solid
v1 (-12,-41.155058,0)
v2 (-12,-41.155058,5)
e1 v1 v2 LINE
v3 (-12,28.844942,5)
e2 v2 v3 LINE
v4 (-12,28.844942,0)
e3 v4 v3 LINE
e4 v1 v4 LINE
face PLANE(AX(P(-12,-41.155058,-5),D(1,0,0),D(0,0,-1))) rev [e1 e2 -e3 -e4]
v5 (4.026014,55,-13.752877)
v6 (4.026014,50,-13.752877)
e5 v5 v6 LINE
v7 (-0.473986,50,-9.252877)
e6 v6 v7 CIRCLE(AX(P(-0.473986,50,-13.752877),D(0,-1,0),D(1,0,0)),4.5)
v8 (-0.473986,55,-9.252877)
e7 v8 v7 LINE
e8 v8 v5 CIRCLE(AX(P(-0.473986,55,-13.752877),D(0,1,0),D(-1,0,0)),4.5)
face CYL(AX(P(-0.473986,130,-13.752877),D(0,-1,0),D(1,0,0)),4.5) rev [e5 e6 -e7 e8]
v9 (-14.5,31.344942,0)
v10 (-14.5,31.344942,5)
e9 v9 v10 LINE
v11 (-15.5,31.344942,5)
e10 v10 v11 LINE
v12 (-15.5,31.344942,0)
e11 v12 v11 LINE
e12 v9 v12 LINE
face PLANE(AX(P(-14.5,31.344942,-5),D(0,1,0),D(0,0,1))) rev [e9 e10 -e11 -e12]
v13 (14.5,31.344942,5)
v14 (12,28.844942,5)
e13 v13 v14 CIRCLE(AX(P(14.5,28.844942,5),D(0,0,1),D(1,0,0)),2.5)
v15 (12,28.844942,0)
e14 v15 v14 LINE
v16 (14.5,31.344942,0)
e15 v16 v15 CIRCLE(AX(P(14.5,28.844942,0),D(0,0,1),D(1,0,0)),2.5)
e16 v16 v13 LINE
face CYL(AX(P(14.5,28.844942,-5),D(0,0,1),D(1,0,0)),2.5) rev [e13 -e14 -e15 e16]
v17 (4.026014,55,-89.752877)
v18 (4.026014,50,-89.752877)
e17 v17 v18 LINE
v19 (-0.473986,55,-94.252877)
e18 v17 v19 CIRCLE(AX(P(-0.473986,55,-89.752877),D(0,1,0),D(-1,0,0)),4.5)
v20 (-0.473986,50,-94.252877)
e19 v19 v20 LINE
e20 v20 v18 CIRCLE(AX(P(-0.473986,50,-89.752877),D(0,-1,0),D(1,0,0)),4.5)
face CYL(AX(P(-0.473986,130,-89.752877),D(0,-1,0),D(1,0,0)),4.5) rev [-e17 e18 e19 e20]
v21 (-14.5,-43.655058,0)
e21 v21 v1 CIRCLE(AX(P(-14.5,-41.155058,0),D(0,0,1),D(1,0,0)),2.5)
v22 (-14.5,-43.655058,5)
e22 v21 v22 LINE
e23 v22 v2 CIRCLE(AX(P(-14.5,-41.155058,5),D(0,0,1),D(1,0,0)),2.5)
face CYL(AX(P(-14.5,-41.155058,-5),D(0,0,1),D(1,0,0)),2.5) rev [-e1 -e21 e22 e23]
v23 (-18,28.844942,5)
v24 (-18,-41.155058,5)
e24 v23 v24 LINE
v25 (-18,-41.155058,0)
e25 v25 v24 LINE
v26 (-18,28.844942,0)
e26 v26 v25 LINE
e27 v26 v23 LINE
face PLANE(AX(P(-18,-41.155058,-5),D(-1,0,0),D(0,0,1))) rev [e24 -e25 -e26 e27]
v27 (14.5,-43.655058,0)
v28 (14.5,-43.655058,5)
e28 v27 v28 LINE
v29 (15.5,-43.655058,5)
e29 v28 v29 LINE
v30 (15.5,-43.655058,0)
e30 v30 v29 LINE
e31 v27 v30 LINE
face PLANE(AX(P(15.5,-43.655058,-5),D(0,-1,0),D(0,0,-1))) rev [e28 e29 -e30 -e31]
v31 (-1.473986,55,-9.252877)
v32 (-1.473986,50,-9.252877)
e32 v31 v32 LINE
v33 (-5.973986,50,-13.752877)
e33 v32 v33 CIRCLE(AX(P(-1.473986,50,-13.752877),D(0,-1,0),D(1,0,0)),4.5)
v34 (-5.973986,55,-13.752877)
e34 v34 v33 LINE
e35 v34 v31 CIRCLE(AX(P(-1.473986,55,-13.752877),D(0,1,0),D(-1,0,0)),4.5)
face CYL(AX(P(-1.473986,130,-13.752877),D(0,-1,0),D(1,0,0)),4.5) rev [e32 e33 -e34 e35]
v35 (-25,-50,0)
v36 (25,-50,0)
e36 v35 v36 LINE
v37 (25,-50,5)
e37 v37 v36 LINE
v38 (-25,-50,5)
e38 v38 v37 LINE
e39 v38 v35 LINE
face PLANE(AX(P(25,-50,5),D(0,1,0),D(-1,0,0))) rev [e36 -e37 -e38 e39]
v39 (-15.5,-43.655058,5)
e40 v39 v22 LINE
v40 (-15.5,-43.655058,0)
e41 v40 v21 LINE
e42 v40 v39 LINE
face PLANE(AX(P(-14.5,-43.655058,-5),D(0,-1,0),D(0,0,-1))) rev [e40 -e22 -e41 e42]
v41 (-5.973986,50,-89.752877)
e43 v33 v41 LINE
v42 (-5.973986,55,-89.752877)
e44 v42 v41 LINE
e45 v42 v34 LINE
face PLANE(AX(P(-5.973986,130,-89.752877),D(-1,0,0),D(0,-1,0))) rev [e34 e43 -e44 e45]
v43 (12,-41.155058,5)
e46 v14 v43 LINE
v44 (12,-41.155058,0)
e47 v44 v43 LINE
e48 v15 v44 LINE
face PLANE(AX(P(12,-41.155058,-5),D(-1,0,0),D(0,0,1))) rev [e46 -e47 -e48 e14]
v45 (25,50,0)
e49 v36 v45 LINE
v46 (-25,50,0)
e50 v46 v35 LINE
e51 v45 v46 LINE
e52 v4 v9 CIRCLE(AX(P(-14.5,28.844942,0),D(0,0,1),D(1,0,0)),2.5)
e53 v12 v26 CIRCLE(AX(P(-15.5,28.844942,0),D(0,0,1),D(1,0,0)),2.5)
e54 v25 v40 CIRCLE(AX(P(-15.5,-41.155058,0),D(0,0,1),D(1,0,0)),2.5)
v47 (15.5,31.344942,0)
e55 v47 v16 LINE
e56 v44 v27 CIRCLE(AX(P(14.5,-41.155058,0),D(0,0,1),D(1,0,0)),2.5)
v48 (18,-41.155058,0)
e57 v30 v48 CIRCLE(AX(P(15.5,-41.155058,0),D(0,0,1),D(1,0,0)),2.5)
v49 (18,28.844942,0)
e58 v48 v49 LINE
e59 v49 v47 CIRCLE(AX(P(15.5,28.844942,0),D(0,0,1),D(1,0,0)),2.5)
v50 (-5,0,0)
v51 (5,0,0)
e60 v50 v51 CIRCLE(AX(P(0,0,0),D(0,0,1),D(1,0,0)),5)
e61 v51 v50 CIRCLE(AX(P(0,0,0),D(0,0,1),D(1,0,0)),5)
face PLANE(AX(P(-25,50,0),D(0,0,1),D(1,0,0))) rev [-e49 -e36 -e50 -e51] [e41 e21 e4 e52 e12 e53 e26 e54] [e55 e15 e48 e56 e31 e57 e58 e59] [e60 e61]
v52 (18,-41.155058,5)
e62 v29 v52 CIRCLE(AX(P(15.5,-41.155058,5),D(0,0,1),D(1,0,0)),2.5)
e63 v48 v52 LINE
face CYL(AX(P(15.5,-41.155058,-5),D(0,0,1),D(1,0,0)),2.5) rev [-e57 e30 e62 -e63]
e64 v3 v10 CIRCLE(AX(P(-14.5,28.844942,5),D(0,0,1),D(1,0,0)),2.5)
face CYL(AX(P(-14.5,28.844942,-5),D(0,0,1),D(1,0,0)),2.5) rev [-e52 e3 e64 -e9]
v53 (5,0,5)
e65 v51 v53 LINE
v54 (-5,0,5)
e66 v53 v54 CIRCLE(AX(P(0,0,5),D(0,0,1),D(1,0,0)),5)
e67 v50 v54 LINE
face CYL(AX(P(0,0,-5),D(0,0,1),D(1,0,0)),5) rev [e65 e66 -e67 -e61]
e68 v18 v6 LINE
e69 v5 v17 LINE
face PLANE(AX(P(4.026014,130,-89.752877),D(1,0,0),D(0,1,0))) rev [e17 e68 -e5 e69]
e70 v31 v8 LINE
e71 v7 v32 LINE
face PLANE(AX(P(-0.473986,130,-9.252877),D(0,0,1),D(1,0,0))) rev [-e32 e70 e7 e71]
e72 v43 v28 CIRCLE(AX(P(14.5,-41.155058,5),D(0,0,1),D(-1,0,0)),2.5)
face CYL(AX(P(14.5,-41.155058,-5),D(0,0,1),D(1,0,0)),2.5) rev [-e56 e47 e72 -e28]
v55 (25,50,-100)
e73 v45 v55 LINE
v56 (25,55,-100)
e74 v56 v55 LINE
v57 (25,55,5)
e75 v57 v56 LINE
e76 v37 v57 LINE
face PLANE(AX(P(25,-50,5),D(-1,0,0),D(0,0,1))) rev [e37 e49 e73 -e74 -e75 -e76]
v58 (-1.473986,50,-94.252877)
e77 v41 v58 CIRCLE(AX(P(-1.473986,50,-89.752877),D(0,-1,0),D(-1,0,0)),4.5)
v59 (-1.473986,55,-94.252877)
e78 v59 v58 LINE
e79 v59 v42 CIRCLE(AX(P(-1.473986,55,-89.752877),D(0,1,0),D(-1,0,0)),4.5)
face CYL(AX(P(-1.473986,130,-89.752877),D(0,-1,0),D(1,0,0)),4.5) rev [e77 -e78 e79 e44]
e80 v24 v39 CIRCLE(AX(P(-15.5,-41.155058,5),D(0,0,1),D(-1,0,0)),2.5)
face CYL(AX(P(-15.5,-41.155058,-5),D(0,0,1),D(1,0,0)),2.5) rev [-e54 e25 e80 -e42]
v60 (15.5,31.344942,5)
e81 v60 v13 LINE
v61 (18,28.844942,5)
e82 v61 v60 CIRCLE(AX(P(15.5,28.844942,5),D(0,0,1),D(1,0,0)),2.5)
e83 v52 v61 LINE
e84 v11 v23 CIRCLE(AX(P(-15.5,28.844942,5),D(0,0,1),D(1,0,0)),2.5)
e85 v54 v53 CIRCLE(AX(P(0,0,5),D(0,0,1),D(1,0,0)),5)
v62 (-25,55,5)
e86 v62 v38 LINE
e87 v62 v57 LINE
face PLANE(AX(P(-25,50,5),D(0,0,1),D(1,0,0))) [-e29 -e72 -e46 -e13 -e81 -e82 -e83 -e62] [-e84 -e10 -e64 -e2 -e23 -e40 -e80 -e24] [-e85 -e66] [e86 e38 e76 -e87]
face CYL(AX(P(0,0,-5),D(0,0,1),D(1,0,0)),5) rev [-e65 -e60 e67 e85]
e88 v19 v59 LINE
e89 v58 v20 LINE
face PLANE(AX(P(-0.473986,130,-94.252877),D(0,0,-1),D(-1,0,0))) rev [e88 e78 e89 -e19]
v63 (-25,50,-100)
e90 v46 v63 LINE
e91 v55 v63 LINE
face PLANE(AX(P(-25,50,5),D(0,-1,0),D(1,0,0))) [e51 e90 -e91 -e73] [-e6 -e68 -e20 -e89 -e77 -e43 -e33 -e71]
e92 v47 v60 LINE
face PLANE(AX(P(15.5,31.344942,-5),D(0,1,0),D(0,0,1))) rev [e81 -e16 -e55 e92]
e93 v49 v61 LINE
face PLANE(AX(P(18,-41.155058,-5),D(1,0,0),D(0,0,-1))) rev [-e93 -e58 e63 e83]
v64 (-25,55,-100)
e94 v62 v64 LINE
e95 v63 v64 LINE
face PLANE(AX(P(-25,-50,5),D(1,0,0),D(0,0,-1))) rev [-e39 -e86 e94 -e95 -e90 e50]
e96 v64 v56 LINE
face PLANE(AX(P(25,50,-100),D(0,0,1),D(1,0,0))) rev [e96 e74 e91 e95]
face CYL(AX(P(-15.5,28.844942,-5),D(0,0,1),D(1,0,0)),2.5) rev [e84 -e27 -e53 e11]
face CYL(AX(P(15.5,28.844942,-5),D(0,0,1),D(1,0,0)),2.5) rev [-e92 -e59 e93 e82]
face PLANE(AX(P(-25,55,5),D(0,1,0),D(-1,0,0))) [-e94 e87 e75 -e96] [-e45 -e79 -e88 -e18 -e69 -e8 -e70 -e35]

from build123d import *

# Parameters (mm, degrees)
SKETCH1_W                = 50
SKETCH1_H                = 100
BOSS_EXTRUDE1_DEPTH      = 5
CUT_EXTRUDE1_DEPTH       = 10
SKETCH3_R                = 5
CUT_EXTRUDE2_DEPTH       = 10
BOSS_EXTRUDE2_DEPTH      = 100
BOSS_EXTRUDE2_DEPTH_BACK = 5
SKETCH4_W                = 50
SKETCH4_H                = 5
CUT_EXTRUDE3_DEPTH       = 80


with BuildPart() as part:
    # Sketch1 → Boss-Extrude1 (new body)
    with BuildSketch(Plane.XY):
        Rectangle(SKETCH1_W, SKETCH1_H)
    extrude(amount=BOSS_EXTRUDE1_DEPTH)

    # Sketch2 → Cut-Extrude1 (cut)
    with BuildSketch(Plane.XY.offset(5)):
        with BuildLine():
            Line((-14.5, -43.655057898), (-15.5, -43.655057898))
            ThreePointArc((-15.5, -43.655057898), (-17.267766953, -42.922824851), (-18, -41.155057898))
            Line((-18, -41.155057898), (-18, 28.844942102))
            ThreePointArc((-18, 28.844942102), (-17.267766953, 30.612709055), (-15.5, 31.344942102))
            Line((-15.5, 31.344942102), (-14.5, 31.344942102))
            ThreePointArc((-14.5, 31.344942102), (-12.732233047, 30.612709055), (-12, 28.844942102))
            Line((-12, 28.844942102), (-12, -41.155057898))
            ThreePointArc((-12, -41.155057898), (-12.732233047, -42.922824851), (-14.5, -43.655057898))
        make_face()
        with BuildLine():
            Line((15.5, -43.655057898), (14.5, -43.655057898))
            ThreePointArc((14.5, -43.655057898), (12.732233047, -42.922824851), (12, -41.155057898))
            Line((12, -41.155057898), (12, 28.844942102))
            ThreePointArc((12, 28.844942102), (12.732233047, 30.612709055), (14.5, 31.344942102))
            Line((14.5, 31.344942102), (15.5, 31.344942102))
            ThreePointArc((15.5, 31.344942102), (17.267766953, 30.612709055), (18, 28.844942102))
            Line((18, 28.844942102), (18, -41.155057898))
            ThreePointArc((18, -41.155057898), (17.267766953, -42.922824851), (15.5, -43.655057898))
        make_face()
    extrude(amount=-CUT_EXTRUDE1_DEPTH, mode=Mode.SUBTRACT)

    # Sketch3 → Cut-Extrude2 (cut)
    with BuildSketch(Plane.XY.offset(5)):
        Circle(SKETCH3_R)
    extrude(amount=-CUT_EXTRUDE2_DEPTH, mode=Mode.SUBTRACT)

    # Sketch4 → Boss-Extrude2 (add, two sides: drawn at the far end of the back side and taken through both)
    with BuildSketch(Plane(origin=(0, 0, 0), x_dir=(-1, 0, 0), z_dir=(0, 0, -1)).offset(-BOSS_EXTRUDE2_DEPTH_BACK)):
        with Locations((0, 52.5)):
            Rectangle(SKETCH4_W, SKETCH4_H)
    extrude(amount=BOSS_EXTRUDE2_DEPTH + BOSS_EXTRUDE2_DEPTH_BACK)

    # Sketch5 → Cut-Extrude3 (cut)
    with BuildSketch(Plane.XZ.offset(-50)):
        with BuildLine():
            Line((-0.473985761, -94.252877225), (-1.473985761, -94.252877225))
            ThreePointArc((-1.473985761, -94.252877225), (-4.655966276, -92.934857741), (-5.973985761, -89.752877225))
            Line((-5.973985761, -89.752877225), (-5.973985761, -13.752877225))
            ThreePointArc((-5.973985761, -13.752877225), (-4.655966276, -10.57089671), (-1.473985761, -9.252877225))
            Line((-1.473985761, -9.252877225), (-0.473985761, -9.252877225))
            ThreePointArc((-0.473985761, -9.252877225), (2.707994755, -10.57089671), (4.026014239, -13.752877225))
            Line((4.026014239, -13.752877225), (4.026014239, -89.752877225))
            ThreePointArc((4.026014239, -89.752877225), (2.707994755, -92.934857741), (-0.473985761, -94.252877225))
        make_face()
    extrude(amount=-CUT_EXTRUDE3_DEPTH, mode=Mode.SUBTRACT)


solid = part.part
